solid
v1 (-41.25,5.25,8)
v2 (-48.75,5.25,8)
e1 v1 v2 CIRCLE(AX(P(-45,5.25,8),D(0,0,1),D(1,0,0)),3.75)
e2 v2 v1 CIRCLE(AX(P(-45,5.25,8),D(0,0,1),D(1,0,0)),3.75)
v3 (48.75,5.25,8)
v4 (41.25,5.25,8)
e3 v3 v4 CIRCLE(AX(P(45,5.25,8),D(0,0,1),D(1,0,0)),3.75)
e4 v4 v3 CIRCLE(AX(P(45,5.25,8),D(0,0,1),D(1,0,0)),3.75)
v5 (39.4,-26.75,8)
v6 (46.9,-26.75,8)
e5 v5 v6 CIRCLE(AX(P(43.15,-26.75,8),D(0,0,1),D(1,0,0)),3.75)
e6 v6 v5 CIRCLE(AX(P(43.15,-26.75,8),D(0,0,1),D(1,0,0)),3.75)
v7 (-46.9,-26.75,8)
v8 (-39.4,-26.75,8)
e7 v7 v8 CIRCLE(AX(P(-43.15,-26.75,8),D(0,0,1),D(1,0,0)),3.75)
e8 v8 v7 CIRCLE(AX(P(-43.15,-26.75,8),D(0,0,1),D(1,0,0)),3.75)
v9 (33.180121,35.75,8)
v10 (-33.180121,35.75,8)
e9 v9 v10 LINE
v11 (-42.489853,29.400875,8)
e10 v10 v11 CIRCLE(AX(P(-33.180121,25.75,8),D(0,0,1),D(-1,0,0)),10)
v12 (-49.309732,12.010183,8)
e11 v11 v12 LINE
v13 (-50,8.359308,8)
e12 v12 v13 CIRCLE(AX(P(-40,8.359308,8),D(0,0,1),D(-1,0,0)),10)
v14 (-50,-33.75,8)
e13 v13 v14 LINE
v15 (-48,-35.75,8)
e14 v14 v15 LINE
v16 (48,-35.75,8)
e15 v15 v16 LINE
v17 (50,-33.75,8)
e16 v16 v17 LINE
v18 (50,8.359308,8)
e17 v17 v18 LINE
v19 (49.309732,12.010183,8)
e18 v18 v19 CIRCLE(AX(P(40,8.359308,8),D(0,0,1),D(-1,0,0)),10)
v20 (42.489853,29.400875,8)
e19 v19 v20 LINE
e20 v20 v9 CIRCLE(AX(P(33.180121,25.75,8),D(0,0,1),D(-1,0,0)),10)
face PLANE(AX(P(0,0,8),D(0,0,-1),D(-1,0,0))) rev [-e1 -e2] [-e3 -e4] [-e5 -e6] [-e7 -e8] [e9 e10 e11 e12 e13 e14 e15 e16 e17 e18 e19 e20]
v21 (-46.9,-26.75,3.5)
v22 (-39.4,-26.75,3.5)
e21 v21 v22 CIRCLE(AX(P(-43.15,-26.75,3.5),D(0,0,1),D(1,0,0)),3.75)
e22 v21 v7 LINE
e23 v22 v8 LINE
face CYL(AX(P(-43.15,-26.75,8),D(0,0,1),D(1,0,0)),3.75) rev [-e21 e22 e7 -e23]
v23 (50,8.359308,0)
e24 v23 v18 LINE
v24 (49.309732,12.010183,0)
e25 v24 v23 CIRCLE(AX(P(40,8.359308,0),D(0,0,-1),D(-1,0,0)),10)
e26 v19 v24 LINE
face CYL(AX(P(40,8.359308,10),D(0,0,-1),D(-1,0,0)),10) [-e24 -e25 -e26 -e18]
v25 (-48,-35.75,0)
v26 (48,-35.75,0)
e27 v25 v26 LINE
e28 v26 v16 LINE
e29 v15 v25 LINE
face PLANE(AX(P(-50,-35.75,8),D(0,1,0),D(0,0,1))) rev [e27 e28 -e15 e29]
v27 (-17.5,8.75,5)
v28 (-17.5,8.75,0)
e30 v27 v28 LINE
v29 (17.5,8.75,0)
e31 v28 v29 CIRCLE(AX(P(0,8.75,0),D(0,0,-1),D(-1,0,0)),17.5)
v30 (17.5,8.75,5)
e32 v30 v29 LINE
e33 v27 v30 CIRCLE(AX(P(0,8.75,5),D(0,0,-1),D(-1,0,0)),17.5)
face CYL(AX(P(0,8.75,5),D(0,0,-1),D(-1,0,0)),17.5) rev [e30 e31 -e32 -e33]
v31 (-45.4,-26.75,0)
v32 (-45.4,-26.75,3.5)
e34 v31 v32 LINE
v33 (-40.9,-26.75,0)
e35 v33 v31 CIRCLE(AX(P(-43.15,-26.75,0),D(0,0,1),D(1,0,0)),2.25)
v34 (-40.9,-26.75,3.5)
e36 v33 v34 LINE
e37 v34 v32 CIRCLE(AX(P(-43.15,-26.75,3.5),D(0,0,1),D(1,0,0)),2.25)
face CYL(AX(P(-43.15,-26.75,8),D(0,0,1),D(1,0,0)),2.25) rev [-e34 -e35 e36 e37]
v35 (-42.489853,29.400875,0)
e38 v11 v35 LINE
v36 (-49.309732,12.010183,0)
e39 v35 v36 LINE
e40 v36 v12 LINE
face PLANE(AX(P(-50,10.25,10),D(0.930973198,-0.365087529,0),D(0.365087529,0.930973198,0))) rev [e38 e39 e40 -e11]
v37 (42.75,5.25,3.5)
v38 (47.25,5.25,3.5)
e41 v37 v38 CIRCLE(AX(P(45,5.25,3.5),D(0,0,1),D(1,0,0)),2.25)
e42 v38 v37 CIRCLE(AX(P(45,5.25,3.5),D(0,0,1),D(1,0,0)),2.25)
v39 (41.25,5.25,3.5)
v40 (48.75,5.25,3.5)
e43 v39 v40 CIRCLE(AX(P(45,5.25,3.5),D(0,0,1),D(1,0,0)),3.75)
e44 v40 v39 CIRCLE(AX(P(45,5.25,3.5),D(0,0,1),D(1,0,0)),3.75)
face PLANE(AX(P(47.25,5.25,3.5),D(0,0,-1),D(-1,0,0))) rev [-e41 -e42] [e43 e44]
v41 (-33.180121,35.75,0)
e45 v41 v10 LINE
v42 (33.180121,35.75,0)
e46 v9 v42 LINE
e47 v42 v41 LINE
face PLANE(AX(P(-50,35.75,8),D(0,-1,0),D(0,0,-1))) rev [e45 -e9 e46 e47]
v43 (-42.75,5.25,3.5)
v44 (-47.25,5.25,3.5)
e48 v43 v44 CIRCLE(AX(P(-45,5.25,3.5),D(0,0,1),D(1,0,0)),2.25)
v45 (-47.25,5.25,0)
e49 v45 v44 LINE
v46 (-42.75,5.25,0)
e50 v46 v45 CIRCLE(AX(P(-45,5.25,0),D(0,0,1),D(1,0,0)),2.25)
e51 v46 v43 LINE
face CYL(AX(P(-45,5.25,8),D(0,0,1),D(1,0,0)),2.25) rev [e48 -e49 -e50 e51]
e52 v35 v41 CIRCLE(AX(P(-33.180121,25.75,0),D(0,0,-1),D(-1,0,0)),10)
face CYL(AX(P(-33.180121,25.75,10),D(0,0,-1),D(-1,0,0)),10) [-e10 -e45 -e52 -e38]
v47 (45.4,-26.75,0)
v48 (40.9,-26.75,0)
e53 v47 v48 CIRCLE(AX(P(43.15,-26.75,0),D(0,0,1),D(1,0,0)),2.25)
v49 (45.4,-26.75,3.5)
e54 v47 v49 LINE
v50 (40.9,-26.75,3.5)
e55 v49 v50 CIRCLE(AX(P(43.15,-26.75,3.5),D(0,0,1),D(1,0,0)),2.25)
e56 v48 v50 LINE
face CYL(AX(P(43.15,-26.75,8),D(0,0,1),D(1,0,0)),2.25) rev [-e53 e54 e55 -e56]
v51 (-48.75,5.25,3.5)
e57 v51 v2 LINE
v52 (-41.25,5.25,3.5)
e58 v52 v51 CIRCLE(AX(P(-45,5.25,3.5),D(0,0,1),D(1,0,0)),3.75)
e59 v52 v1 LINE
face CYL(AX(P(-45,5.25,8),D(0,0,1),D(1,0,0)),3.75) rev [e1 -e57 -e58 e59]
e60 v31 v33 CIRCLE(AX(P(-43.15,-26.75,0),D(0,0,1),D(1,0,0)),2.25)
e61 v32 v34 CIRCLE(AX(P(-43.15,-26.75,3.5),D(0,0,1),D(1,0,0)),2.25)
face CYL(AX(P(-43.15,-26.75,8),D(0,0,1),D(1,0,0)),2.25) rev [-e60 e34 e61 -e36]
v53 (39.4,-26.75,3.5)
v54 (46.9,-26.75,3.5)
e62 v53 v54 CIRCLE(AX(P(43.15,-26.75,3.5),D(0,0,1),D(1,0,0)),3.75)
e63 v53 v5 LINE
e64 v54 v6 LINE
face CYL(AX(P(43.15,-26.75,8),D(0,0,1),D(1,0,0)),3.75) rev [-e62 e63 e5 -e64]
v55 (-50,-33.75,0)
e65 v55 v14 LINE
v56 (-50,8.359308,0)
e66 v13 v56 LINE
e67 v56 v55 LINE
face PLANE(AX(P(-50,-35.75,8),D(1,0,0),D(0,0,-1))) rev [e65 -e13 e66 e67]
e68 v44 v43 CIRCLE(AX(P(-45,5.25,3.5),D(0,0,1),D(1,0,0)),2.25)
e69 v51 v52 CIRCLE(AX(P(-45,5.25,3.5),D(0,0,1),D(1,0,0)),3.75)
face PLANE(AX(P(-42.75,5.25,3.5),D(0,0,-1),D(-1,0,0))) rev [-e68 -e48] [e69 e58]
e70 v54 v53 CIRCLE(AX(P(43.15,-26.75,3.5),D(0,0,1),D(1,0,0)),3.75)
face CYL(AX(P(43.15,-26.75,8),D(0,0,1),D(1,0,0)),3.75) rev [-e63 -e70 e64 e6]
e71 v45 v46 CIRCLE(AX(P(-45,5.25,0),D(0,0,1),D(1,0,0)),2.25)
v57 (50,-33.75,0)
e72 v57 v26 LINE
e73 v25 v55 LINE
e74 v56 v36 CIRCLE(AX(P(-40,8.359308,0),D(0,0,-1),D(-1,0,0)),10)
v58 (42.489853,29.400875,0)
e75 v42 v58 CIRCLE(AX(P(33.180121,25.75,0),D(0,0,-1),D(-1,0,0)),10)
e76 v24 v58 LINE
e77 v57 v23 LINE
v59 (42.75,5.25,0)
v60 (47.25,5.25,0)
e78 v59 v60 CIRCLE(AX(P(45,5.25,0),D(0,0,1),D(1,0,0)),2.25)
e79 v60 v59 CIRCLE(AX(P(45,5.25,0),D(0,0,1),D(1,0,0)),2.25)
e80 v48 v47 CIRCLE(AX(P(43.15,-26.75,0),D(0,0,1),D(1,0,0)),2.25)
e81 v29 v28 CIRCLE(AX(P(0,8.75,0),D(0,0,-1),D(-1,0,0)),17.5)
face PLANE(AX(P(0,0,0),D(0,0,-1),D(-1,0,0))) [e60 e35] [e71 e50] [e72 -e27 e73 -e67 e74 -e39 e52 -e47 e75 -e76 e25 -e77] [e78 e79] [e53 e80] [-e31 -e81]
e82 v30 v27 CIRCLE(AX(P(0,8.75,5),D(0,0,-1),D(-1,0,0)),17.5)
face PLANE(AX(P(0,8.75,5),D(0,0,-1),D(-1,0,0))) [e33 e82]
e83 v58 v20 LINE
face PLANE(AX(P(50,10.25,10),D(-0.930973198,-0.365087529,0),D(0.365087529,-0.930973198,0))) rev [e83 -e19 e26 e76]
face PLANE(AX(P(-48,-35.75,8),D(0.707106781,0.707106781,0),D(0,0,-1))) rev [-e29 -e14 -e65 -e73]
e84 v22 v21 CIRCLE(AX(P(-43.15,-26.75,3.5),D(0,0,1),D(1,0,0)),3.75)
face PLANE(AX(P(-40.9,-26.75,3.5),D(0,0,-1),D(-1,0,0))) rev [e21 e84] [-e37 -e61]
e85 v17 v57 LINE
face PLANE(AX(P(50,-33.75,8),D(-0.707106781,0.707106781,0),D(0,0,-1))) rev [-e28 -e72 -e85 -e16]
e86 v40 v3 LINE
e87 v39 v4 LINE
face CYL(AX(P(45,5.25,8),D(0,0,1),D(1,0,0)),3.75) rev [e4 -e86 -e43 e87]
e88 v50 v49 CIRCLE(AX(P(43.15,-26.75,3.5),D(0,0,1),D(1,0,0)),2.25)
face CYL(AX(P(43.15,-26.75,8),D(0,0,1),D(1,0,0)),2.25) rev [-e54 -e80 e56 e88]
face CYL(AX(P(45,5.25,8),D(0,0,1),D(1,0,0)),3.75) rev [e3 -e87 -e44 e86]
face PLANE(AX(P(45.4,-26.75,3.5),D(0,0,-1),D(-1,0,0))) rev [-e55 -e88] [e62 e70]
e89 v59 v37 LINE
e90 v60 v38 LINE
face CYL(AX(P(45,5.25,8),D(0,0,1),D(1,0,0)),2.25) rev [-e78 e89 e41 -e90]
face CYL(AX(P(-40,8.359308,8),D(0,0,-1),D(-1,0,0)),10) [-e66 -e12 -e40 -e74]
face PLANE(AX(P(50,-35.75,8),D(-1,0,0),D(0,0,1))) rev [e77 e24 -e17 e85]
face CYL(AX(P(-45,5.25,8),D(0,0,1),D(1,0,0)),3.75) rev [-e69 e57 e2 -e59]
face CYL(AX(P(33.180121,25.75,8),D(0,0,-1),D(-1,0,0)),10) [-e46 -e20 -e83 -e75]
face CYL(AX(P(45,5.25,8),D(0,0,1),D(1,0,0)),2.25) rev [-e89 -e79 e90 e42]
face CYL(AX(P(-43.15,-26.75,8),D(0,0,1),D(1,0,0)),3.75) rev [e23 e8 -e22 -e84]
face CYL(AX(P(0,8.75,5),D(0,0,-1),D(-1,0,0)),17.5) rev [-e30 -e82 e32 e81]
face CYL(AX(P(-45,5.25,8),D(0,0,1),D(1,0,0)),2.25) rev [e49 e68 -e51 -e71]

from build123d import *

# Parameters (mm, degrees)
SKETCH_1_W                = 100
SKETCH_1_H                = 71.5
EXTRUDE_1_DEPTH           = 8
CUT_EXTRUDE_1_DEPTH       = 10
FILLET_1_R                = 10
CHAMFER_2_SIZE            = 2
SKETCH_4_R                = 17.5
CUT_EXTRUDE_2_DEPTH       = 5
HOLE_WIZARD_1_D           = 4.5
HOLE_WIZARD_1_CBORE_D     = 7.5
HOLE_WIZARD_1_CBORE_DEPTH = 4.5


with BuildPart() as part:
    # 草图1 → 凸台-拉伸1 (new body)
    with BuildSketch(Plane.XY):
        Rectangle(SKETCH_1_W, SKETCH_1_H)
    extrude(amount=EXTRUDE_1_DEPTH)

    # 草图3 → 切除-拉伸1 (cut)
    with BuildSketch(Plane(origin=(0, 0, 0), x_dir=(-1, 0, 0), z_dir=(0, 0, -1))):
        Polygon((-50, 10.25), (-40, 35.75), (-50, 35.75), align=None)
        Polygon((50, 35.75), (50, 10.25), (40, 35.75), align=None)
    extrude(amount=-CUT_EXTRUDE_1_DEPTH, mode=Mode.SUBTRACT)

    # 圆角1
    fillet_1_edges = [part.edges().sort_by_distance(p)[0] for p in [
        (50, 10.25, 4),
        (40, 35.75, 4),
        (-40, 35.75, 4),
        (-50, 10.25, 4),
    ]]
    fillet(fillet_1_edges, radius=FILLET_1_R)

    # 倒角2
    chamfer_2_edges = [part.edges().sort_by_distance(p)[0] for p in [
        (50, -35.75, 4),
        (-50, -35.75, 4),
    ]]
    chamfer(chamfer_2_edges, length=CHAMFER_2_SIZE)

    # 草图4 → 切除-拉伸2 (cut)
    with BuildSketch(Plane(origin=(0, 0, 0), x_dir=(-1, 0, 0), z_dir=(0, 0, -1))):
        with Locations((0, 8.75)):
            Circle(SKETCH_4_R)
    extrude(amount=-CUT_EXTRUDE_2_DEPTH, mode=Mode.SUBTRACT)

    # 打孔尺寸(%根据)内六角圆柱头螺钉的类型1 (through all)
    with Locations(Plane.XY.offset(8)):
        with Locations((-45, 5.25), (-43.15, -26.75), (45, 5.25), (43.15, -26.75)):
            CounterBoreHole(HOLE_WIZARD_1_D / 2, HOLE_WIZARD_1_CBORE_D / 2, HOLE_WIZARD_1_CBORE_DEPTH)


solid = part.part
